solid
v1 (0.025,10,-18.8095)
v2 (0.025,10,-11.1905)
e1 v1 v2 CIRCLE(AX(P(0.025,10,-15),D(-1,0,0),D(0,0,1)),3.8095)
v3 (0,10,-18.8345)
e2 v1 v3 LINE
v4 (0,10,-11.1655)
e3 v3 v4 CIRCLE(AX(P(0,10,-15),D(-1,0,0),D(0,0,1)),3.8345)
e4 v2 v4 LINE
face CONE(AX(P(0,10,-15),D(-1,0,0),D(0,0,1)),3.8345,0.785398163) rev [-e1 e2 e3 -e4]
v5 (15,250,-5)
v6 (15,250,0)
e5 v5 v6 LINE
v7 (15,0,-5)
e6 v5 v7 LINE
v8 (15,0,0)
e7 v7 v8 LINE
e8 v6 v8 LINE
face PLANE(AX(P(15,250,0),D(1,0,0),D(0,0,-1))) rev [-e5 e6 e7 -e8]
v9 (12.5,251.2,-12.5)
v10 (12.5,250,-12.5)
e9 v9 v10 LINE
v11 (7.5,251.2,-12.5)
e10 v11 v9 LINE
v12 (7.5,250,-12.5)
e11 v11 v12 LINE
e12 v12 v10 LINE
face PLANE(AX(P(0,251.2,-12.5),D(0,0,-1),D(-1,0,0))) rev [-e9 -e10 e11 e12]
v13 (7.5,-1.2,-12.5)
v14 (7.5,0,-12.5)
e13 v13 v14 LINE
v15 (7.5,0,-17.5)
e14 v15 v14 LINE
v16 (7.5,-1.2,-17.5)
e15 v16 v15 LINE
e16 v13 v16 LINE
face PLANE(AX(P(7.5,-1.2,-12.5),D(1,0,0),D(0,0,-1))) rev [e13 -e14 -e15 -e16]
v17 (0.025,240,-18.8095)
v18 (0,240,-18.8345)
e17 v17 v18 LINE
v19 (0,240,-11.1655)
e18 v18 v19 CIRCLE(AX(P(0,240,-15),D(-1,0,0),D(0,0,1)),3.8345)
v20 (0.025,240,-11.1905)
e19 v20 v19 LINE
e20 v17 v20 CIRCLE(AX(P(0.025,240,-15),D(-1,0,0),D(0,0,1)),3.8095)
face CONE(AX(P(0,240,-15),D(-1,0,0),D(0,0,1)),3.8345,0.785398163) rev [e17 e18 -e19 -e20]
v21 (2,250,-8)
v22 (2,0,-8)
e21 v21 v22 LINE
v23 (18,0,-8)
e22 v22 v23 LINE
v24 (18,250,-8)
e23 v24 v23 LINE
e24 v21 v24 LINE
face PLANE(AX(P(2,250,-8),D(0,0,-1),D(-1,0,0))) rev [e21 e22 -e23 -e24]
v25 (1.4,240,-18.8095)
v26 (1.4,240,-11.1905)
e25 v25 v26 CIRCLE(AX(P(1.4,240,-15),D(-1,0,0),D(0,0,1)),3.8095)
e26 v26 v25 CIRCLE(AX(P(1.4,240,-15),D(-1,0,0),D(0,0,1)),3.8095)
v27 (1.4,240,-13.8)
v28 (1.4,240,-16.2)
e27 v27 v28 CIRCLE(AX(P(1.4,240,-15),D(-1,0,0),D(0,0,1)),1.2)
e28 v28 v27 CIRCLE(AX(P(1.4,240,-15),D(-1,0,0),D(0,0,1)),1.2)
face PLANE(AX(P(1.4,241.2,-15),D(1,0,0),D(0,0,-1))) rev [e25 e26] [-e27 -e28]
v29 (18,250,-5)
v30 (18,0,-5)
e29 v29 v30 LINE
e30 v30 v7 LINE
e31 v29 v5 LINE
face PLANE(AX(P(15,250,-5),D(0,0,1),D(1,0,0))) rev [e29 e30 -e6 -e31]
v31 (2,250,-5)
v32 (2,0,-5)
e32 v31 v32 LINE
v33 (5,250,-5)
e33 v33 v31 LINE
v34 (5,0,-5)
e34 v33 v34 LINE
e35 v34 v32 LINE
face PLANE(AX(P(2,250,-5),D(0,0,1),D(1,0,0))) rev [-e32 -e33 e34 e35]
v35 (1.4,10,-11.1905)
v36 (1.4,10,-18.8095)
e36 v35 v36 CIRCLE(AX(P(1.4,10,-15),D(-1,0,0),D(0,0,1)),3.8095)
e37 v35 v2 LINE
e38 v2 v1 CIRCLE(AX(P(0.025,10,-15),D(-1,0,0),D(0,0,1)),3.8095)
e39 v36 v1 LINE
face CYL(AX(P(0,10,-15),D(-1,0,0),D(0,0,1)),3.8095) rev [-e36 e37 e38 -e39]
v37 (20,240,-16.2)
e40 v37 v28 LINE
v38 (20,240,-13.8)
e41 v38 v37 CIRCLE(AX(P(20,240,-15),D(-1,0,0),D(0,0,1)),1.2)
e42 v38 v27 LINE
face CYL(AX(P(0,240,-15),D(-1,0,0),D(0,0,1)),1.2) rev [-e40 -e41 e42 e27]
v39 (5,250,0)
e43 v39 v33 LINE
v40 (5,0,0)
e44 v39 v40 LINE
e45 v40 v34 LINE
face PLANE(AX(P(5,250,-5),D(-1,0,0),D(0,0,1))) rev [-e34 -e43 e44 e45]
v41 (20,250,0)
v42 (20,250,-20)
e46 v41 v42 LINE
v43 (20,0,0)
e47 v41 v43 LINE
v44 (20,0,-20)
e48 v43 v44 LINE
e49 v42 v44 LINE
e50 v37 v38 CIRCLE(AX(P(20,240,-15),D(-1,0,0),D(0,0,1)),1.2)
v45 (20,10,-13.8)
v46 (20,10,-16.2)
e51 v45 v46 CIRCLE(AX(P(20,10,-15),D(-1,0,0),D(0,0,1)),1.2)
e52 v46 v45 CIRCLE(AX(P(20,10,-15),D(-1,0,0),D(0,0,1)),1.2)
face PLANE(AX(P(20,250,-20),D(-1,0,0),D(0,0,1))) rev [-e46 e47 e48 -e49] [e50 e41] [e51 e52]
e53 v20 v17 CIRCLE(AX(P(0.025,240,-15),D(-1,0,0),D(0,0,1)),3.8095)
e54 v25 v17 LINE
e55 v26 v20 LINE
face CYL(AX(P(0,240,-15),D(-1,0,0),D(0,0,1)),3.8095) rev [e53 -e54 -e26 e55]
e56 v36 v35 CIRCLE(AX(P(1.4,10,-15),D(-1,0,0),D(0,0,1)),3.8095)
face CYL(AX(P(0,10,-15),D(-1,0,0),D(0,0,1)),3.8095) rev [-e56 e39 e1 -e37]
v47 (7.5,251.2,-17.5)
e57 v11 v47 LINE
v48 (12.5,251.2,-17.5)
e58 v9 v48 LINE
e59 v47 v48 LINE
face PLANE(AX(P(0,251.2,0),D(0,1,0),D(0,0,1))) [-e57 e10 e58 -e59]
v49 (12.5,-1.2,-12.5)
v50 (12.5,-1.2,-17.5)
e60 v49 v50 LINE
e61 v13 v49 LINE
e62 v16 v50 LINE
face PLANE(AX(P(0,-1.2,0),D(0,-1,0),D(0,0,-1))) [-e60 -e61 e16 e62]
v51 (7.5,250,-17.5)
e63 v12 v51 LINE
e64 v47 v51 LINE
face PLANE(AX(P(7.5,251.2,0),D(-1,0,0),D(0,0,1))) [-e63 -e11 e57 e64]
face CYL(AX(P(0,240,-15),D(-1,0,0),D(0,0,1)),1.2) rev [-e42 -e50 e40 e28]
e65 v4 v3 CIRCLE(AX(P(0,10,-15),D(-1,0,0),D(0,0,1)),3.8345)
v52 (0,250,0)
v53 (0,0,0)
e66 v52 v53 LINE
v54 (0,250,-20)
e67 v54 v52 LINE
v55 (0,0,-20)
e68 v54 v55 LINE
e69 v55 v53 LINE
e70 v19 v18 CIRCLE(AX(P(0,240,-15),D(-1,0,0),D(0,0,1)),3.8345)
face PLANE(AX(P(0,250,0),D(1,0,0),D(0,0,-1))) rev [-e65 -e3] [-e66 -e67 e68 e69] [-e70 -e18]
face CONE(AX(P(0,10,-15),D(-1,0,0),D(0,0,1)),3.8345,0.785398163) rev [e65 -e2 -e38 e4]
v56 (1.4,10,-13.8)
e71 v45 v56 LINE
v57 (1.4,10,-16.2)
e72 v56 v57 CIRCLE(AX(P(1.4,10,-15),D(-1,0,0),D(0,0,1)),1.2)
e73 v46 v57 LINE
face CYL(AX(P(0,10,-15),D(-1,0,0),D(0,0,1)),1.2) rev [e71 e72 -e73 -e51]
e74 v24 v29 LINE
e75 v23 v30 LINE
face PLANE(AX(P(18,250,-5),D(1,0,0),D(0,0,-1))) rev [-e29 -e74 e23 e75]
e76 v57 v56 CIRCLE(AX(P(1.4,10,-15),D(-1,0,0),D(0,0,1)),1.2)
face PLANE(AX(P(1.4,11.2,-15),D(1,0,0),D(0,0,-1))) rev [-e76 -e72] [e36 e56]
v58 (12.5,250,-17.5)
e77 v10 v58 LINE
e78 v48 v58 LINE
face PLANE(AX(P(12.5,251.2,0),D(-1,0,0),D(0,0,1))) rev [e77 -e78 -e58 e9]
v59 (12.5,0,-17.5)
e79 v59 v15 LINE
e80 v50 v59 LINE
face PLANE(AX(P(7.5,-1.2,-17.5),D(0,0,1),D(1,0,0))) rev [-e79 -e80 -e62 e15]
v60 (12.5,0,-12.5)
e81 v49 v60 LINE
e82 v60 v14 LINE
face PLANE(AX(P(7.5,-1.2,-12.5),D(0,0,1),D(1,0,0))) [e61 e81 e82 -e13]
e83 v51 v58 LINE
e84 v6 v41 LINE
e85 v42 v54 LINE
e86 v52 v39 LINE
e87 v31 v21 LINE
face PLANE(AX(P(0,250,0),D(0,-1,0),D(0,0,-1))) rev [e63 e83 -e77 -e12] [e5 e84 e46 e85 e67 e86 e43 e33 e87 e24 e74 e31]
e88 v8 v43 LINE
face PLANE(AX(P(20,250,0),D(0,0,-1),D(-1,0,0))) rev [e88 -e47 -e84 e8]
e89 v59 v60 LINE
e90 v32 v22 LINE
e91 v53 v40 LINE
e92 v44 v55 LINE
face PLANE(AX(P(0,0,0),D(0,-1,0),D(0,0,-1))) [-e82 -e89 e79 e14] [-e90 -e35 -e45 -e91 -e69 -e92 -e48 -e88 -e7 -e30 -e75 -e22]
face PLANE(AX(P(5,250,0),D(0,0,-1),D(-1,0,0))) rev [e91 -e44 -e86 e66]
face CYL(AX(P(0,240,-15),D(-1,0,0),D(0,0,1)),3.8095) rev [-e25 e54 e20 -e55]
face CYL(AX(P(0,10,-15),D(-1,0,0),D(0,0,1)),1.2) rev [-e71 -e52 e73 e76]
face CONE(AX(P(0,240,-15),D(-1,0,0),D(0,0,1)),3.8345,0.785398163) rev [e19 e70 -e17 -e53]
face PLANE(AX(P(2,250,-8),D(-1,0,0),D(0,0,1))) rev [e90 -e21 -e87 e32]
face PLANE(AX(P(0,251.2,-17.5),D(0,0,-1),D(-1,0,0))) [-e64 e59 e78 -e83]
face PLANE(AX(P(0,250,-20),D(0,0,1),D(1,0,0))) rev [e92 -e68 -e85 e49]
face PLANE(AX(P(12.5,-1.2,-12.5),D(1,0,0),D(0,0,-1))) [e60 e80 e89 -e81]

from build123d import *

# Parameters (mm, degrees)
BOSS_EXTRUDE1_DEPTH                    = 250
CBORE_FOR_M2_HEX_CAP_SCREW1_AT_2_COUNT = 2
CBORE_FOR_M2_HEX_CAP_SCREW1_AT_2_PITCH = 230
SKETCH_5_3_W                           = 5
SKETCH_5_3_H                           = 5
BOSS_EXTRUDE2_DEPTH                    = 1.2
SKETCH_5_3_2_W                         = 5
SKETCH_5_3_2_H                         = 5
BOSS_EXTRUDE3_DEPTH                    = 251.2
CUT_EXTRUDE1_START                     = -10
SKETCH6_R                              = 1.2
CUT_EXTRUDE1_DEPTH                     = 10


with BuildPart() as part:
    # Sketch1 → Boss-Extrude1 (new body)
    with BuildSketch(Plane(origin=(0, 0, 0), x_dir=(1, 0, 0), z_dir=(0, 1, 0))):
        Polygon((0, 0), (0, 20), (20, 20), (20, 0), (15, 0), (15, 5), (18, 5), (18, 8), (2, 8), (2, 5), (5, 5), (5, 0), align=None)
    extrude(amount=BOSS_EXTRUDE1_DEPTH)

    # Sketch4 → CBORE for M2 Hex Cap Screw1 (revolve, cut)
    with BuildSketch(Plane(origin=(0, 10, -15), x_dir=(0, 0, 1), z_dir=(0, 1, 0))):
        Polygon((0, 0), (0, 25.721032743), (1.2, 25), (1.2, 1.4), (3.8095, 1.4), (3.8095, 0.025), (3.8345, 0), align=None)
    cbore_for_m2_hex_cap_screw1 = revolve(axis=Axis((-6.35, 10, -15), (1, 0, 0)), mode=Mode.SUBTRACT)

    # CBORE for M2 Hex Cap Screw1 at 2: CBORE for M2 Hex Cap Screw1 ×2
    with Locations(*[(0, i * CBORE_FOR_M2_HEX_CAP_SCREW1_AT_2_PITCH, 0) for i in range(1, CBORE_FOR_M2_HEX_CAP_SCREW1_AT_2_COUNT)]):
        add(cbore_for_m2_hex_cap_screw1, mode=Mode.SUBTRACT)

    # Sketch 5_3 → Boss-Extrude2 (add)
    with BuildSketch(Plane(origin=(0, 250, 0), x_dir=(1, 0, 0), z_dir=(0, 1, 0))):
        with Locations((10, 15)):
            Rectangle(SKETCH_5_3_W, SKETCH_5_3_H)
    extrude(amount=BOSS_EXTRUDE2_DEPTH)

    # Sketch 5_3 2 → Boss-Extrude3 (add)
    with BuildSketch(Plane(origin=(0, 250, 0), x_dir=(1, 0, 0), z_dir=(0, 1, 0))):
        with Locations((10, 15)):
            Rectangle(SKETCH_5_3_2_W, SKETCH_5_3_2_H)
    extrude(amount=-BOSS_EXTRUDE3_DEPTH)

    # Sketch6 → Cut-Extrude1 (cut)
    with BuildSketch(Plane(origin=(12.5, 0, 0), x_dir=(0, 0, -1), z_dir=(1, 0, 0)).offset(CUT_EXTRUDE1_START)):
        with Locations(Location((15, 240, 0), (0, 0, 180))):
            Circle(SKETCH6_R)
        with Locations(Location((15, 10, 0), (0, 0, 180))):
            Circle(SKETCH6_R)
    extrude(amount=CUT_EXTRUDE1_DEPTH, mode=Mode.SUBTRACT)


solid = part.part
